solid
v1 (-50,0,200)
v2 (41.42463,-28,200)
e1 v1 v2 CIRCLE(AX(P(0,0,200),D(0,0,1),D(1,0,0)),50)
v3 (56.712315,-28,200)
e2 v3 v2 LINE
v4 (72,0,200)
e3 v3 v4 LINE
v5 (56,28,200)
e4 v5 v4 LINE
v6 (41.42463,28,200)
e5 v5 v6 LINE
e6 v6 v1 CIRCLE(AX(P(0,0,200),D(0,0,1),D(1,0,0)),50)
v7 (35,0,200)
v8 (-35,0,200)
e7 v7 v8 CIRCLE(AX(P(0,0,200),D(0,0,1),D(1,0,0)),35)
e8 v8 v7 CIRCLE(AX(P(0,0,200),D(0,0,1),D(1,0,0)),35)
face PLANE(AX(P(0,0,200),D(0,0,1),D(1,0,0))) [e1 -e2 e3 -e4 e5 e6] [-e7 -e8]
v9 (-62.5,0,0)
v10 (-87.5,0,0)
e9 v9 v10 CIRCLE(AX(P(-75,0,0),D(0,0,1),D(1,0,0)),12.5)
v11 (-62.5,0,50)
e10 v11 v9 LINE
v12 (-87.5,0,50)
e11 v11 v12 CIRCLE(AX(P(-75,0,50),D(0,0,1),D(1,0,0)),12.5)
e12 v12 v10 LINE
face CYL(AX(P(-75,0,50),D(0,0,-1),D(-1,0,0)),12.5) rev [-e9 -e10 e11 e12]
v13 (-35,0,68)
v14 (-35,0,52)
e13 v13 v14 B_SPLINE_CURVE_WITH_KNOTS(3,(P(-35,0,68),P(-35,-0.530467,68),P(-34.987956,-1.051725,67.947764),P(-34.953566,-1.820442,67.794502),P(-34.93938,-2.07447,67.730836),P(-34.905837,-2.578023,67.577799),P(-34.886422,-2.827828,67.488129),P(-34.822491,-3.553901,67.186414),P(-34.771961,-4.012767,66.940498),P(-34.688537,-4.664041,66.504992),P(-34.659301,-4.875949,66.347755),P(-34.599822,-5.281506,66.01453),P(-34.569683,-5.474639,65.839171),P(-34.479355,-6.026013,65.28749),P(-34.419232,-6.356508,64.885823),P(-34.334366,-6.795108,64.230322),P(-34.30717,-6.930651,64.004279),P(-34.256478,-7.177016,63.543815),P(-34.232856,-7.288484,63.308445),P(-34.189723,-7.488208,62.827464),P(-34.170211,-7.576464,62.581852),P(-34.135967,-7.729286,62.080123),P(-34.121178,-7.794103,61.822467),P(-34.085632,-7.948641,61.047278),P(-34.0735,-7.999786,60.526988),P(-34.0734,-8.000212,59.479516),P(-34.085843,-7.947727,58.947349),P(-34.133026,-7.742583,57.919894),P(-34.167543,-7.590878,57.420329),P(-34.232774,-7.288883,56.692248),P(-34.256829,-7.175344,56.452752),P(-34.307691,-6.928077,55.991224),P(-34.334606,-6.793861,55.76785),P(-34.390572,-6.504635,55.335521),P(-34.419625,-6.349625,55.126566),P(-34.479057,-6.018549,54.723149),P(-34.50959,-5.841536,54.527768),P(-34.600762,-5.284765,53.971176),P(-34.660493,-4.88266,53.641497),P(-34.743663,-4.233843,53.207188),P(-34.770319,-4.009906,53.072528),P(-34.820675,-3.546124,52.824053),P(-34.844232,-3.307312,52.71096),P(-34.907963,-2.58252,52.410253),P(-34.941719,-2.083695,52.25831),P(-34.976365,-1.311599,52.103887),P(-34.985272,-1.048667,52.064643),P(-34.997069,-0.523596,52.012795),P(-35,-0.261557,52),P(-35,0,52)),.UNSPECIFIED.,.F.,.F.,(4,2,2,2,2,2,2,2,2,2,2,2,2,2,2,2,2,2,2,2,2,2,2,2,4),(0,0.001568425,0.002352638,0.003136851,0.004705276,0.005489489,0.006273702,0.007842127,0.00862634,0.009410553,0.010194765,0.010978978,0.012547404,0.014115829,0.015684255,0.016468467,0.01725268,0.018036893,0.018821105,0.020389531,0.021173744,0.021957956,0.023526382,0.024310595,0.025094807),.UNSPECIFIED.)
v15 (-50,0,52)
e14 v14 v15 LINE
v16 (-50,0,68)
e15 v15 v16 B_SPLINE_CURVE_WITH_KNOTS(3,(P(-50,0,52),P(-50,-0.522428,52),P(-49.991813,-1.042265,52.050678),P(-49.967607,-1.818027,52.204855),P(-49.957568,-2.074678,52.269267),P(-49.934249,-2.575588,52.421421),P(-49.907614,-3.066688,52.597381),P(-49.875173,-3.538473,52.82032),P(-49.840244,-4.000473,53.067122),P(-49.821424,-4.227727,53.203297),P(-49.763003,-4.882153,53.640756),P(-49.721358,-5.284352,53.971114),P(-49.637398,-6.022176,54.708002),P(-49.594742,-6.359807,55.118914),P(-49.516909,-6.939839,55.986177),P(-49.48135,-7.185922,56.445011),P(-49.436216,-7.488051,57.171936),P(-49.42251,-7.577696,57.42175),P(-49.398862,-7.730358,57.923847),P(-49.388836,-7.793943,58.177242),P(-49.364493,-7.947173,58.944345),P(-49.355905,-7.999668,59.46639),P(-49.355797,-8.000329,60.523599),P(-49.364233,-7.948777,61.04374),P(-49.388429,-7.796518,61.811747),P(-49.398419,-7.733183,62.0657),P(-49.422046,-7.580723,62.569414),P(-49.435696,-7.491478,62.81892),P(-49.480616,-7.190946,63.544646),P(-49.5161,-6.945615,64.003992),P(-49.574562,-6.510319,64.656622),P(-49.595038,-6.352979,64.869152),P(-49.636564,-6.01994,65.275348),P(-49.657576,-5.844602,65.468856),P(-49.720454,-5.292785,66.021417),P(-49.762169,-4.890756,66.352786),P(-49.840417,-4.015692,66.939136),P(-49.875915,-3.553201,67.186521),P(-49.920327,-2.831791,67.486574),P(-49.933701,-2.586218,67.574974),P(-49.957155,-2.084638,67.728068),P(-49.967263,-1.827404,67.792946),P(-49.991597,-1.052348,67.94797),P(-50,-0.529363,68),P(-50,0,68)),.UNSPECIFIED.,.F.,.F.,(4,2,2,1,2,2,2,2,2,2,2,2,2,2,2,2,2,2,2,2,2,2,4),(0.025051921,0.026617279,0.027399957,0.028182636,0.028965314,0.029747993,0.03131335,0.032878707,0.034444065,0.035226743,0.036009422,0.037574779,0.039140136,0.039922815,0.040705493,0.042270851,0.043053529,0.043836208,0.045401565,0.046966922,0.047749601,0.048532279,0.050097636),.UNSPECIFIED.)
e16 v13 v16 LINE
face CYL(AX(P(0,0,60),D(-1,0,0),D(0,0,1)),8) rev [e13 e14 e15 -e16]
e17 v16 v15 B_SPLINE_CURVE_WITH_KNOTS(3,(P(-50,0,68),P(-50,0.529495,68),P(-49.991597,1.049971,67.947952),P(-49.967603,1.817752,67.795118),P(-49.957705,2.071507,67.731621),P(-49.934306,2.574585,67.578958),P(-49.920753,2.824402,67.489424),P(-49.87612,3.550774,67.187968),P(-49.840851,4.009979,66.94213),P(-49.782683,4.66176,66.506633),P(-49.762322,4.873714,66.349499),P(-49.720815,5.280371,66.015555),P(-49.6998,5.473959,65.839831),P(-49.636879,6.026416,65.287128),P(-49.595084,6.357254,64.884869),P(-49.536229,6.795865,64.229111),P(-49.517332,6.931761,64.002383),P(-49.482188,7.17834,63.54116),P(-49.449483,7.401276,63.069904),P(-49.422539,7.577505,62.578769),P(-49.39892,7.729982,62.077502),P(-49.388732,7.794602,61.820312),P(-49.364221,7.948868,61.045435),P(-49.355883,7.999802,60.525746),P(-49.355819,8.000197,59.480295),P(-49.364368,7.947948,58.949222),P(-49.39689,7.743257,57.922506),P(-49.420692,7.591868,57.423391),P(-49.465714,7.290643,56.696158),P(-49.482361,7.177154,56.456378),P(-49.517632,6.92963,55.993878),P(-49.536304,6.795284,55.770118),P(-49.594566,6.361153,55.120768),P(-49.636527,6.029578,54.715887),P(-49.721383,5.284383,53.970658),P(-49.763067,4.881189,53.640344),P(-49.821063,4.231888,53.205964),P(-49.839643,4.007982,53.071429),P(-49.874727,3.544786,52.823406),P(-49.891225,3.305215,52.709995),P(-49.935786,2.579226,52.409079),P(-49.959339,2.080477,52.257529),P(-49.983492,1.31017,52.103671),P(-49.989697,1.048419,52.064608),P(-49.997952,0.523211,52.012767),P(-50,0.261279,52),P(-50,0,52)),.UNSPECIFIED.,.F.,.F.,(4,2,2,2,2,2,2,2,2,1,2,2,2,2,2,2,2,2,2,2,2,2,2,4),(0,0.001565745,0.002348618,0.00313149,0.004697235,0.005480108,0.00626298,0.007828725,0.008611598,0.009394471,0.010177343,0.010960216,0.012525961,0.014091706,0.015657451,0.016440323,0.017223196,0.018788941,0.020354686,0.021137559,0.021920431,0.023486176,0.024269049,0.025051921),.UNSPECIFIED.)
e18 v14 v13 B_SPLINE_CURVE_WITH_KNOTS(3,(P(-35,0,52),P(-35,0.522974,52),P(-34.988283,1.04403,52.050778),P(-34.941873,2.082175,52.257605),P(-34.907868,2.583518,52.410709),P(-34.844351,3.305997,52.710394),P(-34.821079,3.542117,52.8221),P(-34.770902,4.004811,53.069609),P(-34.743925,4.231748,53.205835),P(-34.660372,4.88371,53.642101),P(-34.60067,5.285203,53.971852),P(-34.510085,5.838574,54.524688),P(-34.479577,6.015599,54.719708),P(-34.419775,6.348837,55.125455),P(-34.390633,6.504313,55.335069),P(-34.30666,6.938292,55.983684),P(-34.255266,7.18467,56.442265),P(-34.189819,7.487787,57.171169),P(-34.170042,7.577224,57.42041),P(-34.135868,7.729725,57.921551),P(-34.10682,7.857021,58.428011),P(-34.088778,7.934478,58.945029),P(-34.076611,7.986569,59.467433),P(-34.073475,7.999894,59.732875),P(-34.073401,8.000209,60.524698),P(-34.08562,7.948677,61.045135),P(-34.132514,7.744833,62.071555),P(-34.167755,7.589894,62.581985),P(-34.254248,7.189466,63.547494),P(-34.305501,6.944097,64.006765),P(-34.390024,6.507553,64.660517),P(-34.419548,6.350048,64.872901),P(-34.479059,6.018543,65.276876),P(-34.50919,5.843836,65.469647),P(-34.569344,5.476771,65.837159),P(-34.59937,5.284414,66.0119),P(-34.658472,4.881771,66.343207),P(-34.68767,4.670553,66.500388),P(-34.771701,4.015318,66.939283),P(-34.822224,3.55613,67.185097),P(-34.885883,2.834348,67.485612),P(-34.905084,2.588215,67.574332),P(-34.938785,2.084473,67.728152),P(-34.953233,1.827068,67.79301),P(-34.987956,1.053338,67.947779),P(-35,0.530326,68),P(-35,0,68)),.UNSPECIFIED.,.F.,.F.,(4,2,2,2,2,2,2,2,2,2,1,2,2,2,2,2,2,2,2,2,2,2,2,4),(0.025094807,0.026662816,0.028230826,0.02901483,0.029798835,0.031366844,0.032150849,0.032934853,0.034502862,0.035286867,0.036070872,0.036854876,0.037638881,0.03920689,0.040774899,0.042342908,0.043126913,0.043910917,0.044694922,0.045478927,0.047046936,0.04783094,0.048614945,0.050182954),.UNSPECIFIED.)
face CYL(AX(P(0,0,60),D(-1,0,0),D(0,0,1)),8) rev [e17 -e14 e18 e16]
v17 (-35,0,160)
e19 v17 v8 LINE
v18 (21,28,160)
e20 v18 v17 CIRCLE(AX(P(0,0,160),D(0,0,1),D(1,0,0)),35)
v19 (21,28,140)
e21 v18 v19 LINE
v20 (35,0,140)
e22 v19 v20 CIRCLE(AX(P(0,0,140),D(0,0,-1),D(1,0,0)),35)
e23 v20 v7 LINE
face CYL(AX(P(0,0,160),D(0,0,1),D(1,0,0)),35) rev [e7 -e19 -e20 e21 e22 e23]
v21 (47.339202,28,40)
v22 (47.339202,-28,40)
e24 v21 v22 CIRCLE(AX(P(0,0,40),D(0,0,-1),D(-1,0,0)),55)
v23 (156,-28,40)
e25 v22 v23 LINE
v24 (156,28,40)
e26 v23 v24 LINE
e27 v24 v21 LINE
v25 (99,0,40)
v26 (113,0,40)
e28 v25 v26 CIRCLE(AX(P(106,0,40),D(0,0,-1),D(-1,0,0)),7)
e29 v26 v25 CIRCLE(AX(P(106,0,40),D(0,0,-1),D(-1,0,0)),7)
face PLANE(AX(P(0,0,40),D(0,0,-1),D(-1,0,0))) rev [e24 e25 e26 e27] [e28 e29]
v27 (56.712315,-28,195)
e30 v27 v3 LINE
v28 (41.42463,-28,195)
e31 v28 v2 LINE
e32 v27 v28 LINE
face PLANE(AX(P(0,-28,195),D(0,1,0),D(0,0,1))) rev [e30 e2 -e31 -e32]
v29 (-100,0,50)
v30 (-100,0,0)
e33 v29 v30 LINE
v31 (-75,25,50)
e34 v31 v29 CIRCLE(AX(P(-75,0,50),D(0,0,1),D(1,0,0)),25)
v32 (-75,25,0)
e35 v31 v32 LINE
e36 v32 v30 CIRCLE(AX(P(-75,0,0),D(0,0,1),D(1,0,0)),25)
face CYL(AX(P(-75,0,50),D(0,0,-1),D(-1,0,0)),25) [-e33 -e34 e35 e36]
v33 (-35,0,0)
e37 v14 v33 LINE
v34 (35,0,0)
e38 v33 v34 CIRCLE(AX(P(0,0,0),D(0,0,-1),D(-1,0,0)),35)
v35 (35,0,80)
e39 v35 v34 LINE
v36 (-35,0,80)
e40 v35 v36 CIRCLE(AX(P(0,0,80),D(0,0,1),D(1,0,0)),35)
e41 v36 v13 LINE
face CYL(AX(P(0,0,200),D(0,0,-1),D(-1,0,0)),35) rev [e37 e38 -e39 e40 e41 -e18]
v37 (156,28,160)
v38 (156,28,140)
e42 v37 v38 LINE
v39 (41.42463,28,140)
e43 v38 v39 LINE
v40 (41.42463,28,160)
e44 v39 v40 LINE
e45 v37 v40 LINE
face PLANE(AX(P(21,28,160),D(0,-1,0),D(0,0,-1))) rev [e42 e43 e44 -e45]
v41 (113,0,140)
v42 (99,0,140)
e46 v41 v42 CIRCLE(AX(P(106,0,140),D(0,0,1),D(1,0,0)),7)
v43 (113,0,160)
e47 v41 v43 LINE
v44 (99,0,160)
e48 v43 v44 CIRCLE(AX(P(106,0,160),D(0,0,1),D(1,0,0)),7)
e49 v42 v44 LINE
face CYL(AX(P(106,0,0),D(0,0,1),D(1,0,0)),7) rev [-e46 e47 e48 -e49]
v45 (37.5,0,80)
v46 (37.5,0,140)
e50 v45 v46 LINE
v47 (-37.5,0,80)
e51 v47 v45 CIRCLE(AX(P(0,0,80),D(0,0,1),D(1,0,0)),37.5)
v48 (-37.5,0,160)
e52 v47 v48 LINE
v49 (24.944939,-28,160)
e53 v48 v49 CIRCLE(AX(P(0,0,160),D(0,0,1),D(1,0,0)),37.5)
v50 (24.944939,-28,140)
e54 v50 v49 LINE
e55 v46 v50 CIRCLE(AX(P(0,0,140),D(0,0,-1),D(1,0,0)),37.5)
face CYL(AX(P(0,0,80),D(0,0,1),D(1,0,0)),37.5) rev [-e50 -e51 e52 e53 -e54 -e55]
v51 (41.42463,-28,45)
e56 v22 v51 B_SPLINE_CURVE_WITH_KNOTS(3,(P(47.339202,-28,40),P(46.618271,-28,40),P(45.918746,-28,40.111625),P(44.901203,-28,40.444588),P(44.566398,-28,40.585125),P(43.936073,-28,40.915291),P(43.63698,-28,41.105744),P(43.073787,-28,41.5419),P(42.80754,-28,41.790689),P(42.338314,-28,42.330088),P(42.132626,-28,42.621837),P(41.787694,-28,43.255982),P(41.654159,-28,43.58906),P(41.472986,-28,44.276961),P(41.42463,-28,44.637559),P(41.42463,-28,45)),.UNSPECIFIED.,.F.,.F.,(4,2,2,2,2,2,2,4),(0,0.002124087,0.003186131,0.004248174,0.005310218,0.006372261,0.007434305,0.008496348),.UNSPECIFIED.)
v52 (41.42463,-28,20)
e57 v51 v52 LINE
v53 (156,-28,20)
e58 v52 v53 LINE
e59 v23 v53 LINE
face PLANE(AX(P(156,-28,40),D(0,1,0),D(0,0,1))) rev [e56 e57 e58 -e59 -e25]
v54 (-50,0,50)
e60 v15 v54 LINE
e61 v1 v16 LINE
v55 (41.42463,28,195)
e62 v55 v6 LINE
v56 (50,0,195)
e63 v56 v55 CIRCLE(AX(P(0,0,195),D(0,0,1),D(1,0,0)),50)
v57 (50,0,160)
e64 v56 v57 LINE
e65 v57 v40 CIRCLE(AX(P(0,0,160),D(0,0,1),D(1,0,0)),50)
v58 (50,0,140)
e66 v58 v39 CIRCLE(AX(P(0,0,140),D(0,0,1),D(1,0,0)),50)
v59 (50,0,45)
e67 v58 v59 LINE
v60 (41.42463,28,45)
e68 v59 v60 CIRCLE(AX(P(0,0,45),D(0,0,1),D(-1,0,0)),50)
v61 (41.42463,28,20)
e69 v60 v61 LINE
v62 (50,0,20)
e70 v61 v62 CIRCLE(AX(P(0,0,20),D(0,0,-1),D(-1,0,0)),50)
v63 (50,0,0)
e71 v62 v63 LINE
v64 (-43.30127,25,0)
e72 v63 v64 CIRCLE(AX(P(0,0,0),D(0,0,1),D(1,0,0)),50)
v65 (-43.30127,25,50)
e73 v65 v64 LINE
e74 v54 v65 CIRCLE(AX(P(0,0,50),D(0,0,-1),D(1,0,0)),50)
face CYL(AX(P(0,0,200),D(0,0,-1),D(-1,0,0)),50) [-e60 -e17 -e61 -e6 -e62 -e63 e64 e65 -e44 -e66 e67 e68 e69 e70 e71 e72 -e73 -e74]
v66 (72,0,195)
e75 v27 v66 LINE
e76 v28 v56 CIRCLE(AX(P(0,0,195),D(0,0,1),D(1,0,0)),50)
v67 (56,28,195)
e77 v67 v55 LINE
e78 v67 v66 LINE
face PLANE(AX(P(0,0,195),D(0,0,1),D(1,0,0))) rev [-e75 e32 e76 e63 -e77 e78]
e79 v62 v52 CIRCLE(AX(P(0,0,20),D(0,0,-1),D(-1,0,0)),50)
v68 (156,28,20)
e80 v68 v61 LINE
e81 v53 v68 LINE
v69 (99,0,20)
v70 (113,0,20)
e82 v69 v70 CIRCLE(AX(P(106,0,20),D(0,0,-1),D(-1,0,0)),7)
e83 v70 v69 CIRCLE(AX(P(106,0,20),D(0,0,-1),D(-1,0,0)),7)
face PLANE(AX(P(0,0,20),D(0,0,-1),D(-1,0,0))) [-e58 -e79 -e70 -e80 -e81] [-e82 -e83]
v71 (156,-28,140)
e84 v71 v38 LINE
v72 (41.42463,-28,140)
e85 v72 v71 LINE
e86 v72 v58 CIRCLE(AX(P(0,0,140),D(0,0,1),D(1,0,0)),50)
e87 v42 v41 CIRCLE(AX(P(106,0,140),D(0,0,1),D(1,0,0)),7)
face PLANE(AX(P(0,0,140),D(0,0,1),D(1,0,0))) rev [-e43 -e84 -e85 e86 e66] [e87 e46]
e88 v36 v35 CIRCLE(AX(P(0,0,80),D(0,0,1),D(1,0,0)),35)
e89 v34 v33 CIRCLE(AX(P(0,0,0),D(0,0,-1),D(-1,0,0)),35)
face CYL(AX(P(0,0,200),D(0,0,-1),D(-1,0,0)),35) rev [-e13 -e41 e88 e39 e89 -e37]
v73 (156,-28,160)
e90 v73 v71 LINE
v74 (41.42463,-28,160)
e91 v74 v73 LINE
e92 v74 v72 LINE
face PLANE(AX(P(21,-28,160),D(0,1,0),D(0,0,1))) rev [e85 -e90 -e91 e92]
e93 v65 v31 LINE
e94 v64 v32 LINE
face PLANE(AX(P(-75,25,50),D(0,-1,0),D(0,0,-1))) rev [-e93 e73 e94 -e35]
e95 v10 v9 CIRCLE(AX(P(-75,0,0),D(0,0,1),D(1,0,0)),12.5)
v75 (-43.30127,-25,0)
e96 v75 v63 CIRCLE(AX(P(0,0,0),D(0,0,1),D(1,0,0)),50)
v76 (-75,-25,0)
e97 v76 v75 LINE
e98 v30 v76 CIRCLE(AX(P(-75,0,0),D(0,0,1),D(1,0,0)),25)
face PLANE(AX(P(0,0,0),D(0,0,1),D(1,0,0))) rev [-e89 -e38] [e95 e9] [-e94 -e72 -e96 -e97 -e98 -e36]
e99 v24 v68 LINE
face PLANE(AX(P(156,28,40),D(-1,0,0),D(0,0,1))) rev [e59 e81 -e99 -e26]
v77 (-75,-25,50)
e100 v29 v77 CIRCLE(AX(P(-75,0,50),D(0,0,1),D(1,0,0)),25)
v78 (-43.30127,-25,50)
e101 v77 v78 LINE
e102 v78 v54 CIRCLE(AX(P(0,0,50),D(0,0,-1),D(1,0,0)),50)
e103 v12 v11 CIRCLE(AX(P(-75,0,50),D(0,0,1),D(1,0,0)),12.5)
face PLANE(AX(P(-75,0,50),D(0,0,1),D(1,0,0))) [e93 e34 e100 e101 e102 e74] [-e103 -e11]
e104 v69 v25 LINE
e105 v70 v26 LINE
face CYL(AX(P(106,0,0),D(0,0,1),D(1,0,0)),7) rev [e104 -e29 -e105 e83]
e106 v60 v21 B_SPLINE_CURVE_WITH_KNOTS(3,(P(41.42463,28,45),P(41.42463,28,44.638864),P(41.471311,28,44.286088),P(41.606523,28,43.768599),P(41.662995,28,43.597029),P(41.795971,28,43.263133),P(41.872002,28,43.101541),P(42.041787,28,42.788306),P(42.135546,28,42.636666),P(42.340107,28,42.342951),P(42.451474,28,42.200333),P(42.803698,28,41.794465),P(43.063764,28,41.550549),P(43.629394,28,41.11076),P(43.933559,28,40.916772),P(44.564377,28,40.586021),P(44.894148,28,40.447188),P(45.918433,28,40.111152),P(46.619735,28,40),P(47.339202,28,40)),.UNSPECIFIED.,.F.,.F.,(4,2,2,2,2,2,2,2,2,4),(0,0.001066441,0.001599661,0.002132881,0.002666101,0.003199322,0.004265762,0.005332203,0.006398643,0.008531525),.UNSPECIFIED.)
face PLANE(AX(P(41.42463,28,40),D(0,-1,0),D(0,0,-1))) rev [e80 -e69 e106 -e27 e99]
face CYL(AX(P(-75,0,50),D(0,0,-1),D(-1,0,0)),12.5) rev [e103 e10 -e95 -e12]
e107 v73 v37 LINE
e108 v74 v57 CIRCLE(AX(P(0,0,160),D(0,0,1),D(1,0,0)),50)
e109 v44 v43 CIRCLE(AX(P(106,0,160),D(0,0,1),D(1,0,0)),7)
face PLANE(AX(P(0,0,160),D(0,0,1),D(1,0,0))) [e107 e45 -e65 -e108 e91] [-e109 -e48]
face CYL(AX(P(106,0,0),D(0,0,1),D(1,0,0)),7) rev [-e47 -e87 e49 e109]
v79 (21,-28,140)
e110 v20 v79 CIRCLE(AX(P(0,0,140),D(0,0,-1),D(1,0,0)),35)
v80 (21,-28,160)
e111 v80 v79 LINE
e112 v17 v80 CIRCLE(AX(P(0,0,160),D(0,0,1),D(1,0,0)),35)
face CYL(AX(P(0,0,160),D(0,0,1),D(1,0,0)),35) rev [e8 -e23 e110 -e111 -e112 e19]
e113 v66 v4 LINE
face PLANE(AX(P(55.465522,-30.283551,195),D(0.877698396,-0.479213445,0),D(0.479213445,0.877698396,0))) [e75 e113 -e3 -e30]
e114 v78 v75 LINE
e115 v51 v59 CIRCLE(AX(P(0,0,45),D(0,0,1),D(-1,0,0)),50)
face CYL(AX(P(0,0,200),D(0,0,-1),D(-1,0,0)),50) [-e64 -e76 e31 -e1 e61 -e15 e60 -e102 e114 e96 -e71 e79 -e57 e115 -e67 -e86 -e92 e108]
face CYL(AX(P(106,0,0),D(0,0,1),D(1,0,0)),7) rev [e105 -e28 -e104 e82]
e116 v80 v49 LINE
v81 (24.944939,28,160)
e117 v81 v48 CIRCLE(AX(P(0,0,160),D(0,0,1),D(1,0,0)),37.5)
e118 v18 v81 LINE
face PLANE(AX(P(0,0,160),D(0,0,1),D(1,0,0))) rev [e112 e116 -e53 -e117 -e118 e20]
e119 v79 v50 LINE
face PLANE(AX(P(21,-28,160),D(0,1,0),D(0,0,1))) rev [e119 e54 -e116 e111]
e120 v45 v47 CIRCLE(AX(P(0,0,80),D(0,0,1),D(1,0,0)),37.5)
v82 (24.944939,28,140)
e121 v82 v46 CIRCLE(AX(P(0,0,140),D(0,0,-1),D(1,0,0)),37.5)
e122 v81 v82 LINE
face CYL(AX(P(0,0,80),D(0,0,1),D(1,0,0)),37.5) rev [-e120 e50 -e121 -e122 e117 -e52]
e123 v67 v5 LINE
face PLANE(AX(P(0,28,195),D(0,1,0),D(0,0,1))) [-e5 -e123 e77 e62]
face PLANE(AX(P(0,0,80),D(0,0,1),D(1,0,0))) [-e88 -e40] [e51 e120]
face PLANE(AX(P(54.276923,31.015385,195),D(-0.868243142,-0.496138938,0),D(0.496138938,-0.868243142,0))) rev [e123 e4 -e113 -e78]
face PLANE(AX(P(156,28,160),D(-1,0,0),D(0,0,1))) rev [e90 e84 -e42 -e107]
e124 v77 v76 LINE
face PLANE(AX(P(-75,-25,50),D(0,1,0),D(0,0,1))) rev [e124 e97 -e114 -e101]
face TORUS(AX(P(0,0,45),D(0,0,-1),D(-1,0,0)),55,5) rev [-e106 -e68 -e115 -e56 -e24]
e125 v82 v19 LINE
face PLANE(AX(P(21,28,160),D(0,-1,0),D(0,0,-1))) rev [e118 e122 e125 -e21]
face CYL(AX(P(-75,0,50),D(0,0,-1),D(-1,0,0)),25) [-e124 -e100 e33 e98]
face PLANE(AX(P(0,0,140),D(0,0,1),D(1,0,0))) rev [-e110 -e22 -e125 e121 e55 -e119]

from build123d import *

# Parameters (mm, degrees)
BODY_PROFILE_100_R         = 50
HOUSING_BODY_100X200_DEPTH = 200
FRONT_BORE_PROFILE_70_R    = 35
FRONT_BORE_70X40_DEPTH     = 40
INNER_RECESS_PROFILE_75_R  = 37.5
INNER_RECESS_75X80_DEPTH   = 80
THROUGH_BORE_PROFILE_70_R  = 35
THROUGH_BORE_70_DEPTH      = 213.132034356
REAR_START                 = -5
REAR_TAB_5MM_DEPTH         = 5
LUG_PLATES_DEPTH           = 20
LUG_WEB_PROFILE_W          = 114.575369646
LUG_WEB_PROFILE_H          = 56
LUG_WEB_DEPTH              = 20
LUG_PIN_HOLES_PROFILE_14_R = 7
LUG_PIN_HOLES_14_DEPTH     = 229.989082709
LUG_WEB_FILLET_R5_R        = 5
TOP_BOSS_PROFILE_R         = 12.5
TOP_BOSS_DEPTH             = 50
TOP_BOSS_HOLE_PROFILE_16_R = 8
TOP_BOSS_HOLE_16_DEPTH     = 50


with BuildPart() as part:
    # Body Profile Ø100 → Housing Body Ø100x200 (new body)
    with BuildSketch(Plane.XY):
        Circle(BODY_PROFILE_100_R)
    extrude(amount=HOUSING_BODY_100X200_DEPTH)

    # Front Bore Profile Ø70 → Front Bore Ø70x40 (cut)
    with BuildSketch(Plane.XY.offset(200)):
        Circle(FRONT_BORE_PROFILE_70_R)
    extrude(amount=-FRONT_BORE_70X40_DEPTH, mode=Mode.SUBTRACT)

    # Inner Recess Profile Ø75 → Inner Recess Ø75x80 (cut)
    with BuildSketch(Plane.XY.offset(160)):
        Circle(INNER_RECESS_PROFILE_75_R)
    extrude(amount=-INNER_RECESS_75X80_DEPTH, mode=Mode.SUBTRACT)

    # Through Bore Profile Ø70 → Through Bore Ø70 (cut, through all)
    with BuildSketch(Plane(origin=(0, 0, 0), x_dir=(-1, 0, 0), z_dir=(0, 0, -1))):
        with Locations(Location((0, 0, 0), (0, 0, 180))):
            Circle(THROUGH_BORE_PROFILE_70_R)
    extrude(amount=-THROUGH_BORE_70_DEPTH, mode=Mode.SUBTRACT)

    # Rear Tab Profile → Rear Tab 5mm (add)
    with BuildSketch(Plane.XY.offset(200).offset(REAR_START)):
        with BuildLine():
            Line((72, 0), (56, 28))
            Line((56, 28), (41.424630354, 28))
            ThreePointArc((41.424630354, 28), (50, 0), (41.424630354, -28))
            Line((41.424630354, -28), (56.712315177, -28))
            Line((56.712315177, -28), (72, 0))
        make_face()
    extrude(amount=REAR_TAB_5MM_DEPTH)

    # Lug Plates Profile → Lug Plates (add)
    with BuildSketch(Plane.XY.offset(140)):
        with BuildLine():
            Line((21, -28), (156, -28))
            Line((156, -28), (156, 28))
            Line((156, 28), (21, 28))
            ThreePointArc((21, 28), (35, 0), (21, -28))
        make_face()
    extrude(amount=LUG_PLATES_DEPTH)

    # Lug Web Profile → Lug Web (add)
    with BuildSketch(Plane.XY.offset(20)):
        with Locations((98.712315177, 0)):
            Rectangle(LUG_WEB_PROFILE_W, LUG_WEB_PROFILE_H)
    extrude(amount=LUG_WEB_DEPTH)

    # Lug Pin Holes Profile Ø14 → Lug Pin Holes Ø14 (cut, through all)
    with BuildSketch(Plane.XY.offset(160)):
        with Locations(Location((106, 0, 0), (0, 0, 180))):
            Circle(LUG_PIN_HOLES_PROFILE_14_R)
    extrude(amount=-LUG_PIN_HOLES_14_DEPTH, mode=Mode.SUBTRACT)

    # Lug Web Fillet R5
    lug_web_fillet_r5_edges = [part.edges().sort_by_distance(p)[0] for p in [
        (47.808113944, -14.64186604, 40),
    ]]
    fillet(lug_web_fillet_r5_edges, radius=LUG_WEB_FILLET_R5_R)

    # Top Boss Profile → Top Boss (add)
    with BuildSketch(Plane.XY):
        with BuildLine():
            Line((-75, 25), (-43.301270189, 25))
            ThreePointArc((-43.301270189, 25), (-50, 0), (-43.301270189, -25))
            Line((-43.301270189, -25), (-75, -25))
            ThreePointArc((-75, -25), (-100, 0), (-75, 25))
        make_face()
        with Locations((-75, 0)):
            Circle(TOP_BOSS_PROFILE_R, mode=Mode.SUBTRACT)
    extrude(amount=TOP_BOSS_DEPTH)

    # Top Boss Hole Profile Ø16 → Top Boss Hole Ø16 (cut)
    with BuildSketch(Plane(origin=(-50, 0, 0), x_dir=(0, 0, -1), z_dir=(1, 0, 0))):
        with Locations(Location((-60, 0, 0), (0, 0, 180))):
            Circle(TOP_BOSS_HOLE_PROFILE_16_R)
    extrude(amount=TOP_BOSS_HOLE_16_DEPTH, mode=Mode.SUBTRACT)


solid = part.part
